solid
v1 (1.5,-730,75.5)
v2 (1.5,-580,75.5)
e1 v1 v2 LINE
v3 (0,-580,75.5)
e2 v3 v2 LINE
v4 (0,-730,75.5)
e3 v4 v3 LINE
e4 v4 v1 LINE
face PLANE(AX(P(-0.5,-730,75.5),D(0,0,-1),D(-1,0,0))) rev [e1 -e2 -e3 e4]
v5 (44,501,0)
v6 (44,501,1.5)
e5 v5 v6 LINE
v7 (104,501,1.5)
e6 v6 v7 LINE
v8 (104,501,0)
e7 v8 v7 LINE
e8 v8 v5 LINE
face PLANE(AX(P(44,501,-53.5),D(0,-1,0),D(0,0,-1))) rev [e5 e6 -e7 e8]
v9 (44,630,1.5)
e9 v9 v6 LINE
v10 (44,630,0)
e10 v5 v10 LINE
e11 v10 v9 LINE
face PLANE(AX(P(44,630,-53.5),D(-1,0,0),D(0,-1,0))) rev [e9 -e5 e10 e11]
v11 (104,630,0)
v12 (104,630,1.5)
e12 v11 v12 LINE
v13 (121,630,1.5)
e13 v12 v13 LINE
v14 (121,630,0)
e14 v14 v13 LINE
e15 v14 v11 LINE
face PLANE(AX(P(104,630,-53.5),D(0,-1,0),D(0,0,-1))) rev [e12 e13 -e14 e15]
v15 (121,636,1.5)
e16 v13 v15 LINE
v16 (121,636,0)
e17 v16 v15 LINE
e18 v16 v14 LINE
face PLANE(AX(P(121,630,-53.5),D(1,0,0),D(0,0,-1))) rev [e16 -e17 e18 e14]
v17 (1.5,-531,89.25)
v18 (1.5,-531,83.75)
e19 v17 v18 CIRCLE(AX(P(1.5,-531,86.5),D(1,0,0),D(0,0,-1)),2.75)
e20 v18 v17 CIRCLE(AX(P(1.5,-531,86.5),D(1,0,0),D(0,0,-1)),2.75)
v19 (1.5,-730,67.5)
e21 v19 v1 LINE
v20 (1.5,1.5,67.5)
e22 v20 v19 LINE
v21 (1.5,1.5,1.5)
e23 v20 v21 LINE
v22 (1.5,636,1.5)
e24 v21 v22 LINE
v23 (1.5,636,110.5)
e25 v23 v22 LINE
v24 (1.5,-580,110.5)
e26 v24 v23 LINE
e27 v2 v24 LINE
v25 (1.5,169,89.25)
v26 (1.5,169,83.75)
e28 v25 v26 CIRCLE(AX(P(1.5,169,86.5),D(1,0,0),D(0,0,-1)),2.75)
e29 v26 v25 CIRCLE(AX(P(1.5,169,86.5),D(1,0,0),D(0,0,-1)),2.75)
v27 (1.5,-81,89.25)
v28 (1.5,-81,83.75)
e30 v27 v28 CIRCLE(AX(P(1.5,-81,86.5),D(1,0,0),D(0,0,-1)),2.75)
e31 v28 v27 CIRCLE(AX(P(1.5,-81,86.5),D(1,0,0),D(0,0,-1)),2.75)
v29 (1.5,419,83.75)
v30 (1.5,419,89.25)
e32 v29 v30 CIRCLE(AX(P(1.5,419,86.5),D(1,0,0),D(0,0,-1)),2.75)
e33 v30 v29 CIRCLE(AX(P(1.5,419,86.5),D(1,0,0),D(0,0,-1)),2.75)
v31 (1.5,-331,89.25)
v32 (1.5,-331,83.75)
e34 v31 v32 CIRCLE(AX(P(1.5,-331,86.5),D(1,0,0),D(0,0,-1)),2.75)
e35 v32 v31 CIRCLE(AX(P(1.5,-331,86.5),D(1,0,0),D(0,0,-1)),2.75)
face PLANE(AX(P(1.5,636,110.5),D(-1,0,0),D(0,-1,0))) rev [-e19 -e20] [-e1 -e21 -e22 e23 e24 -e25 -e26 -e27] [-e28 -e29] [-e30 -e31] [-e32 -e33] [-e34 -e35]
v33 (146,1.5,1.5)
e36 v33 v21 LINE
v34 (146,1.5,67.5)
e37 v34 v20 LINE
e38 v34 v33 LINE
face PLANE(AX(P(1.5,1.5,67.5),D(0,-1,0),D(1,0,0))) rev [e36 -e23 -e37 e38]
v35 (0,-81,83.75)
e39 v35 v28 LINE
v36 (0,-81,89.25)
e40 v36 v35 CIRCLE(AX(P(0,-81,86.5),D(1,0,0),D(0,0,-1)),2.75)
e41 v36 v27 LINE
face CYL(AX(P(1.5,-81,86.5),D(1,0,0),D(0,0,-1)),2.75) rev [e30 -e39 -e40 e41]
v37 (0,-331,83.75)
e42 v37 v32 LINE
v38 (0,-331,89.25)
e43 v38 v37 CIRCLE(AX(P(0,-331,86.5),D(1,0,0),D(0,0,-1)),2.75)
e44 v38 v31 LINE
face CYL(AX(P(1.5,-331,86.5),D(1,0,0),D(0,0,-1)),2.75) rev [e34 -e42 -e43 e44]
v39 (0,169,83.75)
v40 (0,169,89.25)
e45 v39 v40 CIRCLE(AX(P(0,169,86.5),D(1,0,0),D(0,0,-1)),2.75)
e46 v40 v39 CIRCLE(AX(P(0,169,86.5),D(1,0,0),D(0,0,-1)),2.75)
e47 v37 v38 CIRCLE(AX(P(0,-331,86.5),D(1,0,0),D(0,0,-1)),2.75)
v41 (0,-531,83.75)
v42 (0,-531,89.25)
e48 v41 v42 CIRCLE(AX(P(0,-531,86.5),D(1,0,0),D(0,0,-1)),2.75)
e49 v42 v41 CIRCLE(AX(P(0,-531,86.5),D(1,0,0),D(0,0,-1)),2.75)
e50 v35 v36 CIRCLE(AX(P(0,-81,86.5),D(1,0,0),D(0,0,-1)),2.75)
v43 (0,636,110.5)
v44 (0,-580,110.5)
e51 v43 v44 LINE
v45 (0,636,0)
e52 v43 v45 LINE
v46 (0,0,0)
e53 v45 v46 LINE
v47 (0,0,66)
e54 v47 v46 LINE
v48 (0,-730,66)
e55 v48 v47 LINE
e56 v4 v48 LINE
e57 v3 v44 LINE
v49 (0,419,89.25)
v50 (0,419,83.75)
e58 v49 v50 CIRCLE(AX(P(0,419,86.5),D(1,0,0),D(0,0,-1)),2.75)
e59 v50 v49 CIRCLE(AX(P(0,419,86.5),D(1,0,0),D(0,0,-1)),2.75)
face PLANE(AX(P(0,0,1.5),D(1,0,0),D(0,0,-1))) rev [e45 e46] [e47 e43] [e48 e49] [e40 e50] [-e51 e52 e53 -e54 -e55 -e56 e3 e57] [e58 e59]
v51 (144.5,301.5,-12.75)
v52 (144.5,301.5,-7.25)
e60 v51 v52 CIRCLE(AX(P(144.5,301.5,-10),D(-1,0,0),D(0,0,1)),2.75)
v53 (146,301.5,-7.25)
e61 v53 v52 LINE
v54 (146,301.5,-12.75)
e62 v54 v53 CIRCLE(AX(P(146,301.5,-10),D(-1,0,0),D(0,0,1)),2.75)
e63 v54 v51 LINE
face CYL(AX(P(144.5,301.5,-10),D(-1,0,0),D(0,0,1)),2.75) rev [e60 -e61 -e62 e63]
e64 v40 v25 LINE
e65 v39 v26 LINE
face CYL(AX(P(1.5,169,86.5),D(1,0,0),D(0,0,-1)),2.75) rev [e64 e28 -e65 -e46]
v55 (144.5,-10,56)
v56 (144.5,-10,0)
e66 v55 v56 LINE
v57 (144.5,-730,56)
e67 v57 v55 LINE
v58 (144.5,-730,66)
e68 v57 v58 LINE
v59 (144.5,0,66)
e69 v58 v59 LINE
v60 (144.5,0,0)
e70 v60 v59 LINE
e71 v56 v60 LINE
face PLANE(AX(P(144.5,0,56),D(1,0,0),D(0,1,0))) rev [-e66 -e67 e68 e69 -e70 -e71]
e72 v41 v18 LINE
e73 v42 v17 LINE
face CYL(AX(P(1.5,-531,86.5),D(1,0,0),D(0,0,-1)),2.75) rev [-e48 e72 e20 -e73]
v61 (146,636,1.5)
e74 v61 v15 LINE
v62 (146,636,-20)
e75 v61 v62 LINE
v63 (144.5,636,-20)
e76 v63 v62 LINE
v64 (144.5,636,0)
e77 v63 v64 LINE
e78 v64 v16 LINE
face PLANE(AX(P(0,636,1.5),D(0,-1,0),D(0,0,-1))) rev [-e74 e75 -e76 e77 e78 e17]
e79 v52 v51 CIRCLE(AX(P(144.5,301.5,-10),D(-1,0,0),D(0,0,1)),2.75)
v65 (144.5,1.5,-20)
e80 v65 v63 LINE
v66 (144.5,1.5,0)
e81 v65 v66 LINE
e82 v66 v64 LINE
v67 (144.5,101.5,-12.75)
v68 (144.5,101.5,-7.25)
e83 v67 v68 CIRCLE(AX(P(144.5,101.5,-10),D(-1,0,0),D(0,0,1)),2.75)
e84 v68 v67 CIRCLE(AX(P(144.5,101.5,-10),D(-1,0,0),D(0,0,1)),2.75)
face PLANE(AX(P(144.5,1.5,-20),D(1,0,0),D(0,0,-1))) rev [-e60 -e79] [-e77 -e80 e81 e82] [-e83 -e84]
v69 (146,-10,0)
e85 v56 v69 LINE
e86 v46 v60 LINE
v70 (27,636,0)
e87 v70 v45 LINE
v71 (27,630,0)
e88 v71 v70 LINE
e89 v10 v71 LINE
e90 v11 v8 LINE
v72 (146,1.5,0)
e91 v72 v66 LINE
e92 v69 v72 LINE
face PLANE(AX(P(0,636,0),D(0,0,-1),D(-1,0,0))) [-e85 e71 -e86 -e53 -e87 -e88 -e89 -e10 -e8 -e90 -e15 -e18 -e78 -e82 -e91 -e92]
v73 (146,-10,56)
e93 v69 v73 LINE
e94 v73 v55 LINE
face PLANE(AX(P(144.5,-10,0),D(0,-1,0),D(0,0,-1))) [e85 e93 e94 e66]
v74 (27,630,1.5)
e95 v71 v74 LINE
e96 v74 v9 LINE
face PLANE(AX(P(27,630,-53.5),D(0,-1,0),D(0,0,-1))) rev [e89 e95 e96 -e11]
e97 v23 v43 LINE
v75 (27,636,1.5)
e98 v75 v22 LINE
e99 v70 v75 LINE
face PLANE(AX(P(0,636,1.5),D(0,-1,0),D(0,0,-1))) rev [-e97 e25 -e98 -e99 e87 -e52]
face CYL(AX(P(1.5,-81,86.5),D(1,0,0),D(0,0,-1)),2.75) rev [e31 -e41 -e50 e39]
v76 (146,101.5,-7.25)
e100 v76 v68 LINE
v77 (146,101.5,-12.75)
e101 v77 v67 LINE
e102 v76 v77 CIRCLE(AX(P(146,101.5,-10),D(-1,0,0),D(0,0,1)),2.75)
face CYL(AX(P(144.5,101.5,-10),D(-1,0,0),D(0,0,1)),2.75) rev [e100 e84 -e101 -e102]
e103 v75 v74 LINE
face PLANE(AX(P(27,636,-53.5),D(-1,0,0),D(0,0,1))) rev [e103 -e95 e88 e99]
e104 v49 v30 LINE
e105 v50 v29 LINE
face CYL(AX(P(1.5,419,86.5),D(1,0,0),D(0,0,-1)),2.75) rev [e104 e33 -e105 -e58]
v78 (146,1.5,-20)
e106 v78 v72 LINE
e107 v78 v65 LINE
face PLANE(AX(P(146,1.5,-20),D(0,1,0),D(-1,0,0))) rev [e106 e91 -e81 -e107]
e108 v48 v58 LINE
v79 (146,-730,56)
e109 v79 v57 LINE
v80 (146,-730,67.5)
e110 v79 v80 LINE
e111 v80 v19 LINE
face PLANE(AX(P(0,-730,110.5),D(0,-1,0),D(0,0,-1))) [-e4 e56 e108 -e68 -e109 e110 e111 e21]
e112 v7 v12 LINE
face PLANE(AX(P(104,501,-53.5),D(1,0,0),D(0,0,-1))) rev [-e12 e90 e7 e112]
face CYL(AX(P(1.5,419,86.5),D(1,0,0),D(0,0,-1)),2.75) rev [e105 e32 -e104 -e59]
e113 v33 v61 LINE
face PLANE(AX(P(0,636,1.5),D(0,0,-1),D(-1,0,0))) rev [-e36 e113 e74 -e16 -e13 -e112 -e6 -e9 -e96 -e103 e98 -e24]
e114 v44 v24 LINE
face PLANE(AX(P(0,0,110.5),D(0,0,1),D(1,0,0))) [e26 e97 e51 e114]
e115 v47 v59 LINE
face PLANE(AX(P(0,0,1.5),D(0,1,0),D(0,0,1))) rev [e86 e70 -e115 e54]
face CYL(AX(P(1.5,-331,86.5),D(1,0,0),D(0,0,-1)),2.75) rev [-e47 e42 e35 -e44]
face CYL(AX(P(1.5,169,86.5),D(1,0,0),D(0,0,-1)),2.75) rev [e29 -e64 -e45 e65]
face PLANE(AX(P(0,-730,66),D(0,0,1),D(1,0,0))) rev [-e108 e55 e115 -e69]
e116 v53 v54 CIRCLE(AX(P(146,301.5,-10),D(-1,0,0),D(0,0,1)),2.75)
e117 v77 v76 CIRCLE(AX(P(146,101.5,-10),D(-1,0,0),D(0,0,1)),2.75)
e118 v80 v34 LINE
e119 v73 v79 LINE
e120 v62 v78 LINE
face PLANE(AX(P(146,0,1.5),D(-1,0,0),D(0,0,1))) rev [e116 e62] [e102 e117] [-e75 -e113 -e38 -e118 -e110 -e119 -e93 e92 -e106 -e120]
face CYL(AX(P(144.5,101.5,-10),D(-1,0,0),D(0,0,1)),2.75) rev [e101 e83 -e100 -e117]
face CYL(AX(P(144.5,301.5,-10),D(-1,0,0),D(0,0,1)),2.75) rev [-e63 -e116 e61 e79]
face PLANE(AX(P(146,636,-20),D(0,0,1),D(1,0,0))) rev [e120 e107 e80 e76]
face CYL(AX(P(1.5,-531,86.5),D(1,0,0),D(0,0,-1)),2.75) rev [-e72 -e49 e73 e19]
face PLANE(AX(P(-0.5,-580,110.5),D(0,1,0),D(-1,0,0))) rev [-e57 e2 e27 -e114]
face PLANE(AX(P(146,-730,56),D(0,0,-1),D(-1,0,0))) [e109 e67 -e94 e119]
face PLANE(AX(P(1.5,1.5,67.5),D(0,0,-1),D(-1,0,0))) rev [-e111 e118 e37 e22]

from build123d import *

# Parameters (mm, degrees)
SKETCH_1_W                  = 146
SKETCH_1_H                  = 636
EXTRUDE_1_DEPTH             = 1.5
SKETCH_2_W                  = 1.5
SKETCH_2_H                  = 636
EXTRUDE_2_DEPTH             = 109
SKETCH_4_W                  = 144.5
SKETCH_4_H                  = 1.5
EXTRUDE_4_DEPTH             = 66
EXTRUDE_5_DEPTH             = 730
SKETCH_6_W                  = 1.5
SKETCH_6_H                  = 634.5
EXTRUDE_6_DEPTH             = 20
SKETCH_7_W                  = 1.5
SKETCH_7_H                  = 730
EXTRUDE_7_DEPTH             = 10
SKETCH_8_W                  = 1.5
SKETCH_8_H                  = 56
EXTRUDE_8_DEPTH             = 10
SKETCH_10_W                 = 35
SKETCH_10_H                 = 150
CUT_EXTRUDE_2_DEPTH         = 2
HOLE_WIZARD_5_5_5_5_1_D     = 5.5
HOLE_WIZARD_5_5_5_5_2_D     = 5.5
HOLE_WIZARD_5_5_5_5_2_DEPTH = 1.5
HOLE_WIZARD_5_5_5_5_2_TIP   = 1.652366702
CUT_EXTRUDE_3_DEPTH         = 55


with BuildPart() as part:
    # 草图1 → 凸台-拉伸1 (new body)
    with BuildSketch(Plane.XY):
        with Locations((73, 318)):
            Rectangle(SKETCH_1_W, SKETCH_1_H)
    extrude(amount=EXTRUDE_1_DEPTH)

    # 草图2 → 凸台-拉伸2 (add)
    with BuildSketch(Plane.XY.offset(1.5)):
        with Locations((0.75, 318)):
            Rectangle(SKETCH_2_W, SKETCH_2_H)
    extrude(amount=EXTRUDE_2_DEPTH)

    # 草图4 → 凸台-拉伸4 (add)
    with BuildSketch(Plane.XY.offset(1.5)):
        with Locations((73.75, 0.75)):
            Rectangle(SKETCH_4_W, SKETCH_4_H)
    extrude(amount=EXTRUDE_4_DEPTH)

    # 草图5 → 凸台-拉伸5 (add)
    with BuildSketch(Plane.XZ):
        Polygon((0, 110.5), (0, 66), (146, 66), (146, 67.5), (1.5, 67.5), (1.5, 110.5), align=None)
    extrude(amount=EXTRUDE_5_DEPTH)

    # 草图6 → 凸台-拉伸6 (add)
    with BuildSketch(Plane(origin=(0, 0, 0), x_dir=(-1, 0, 0), z_dir=(0, 0, -1))):
        with Locations((-145.25, 318.75)):
            Rectangle(SKETCH_6_W, SKETCH_6_H)
    extrude(amount=EXTRUDE_6_DEPTH)

    # 草图7 → 凸台-拉伸7 (add)
    with BuildSketch(Plane(origin=(0, 0, 66), x_dir=(-1, 0, 0), z_dir=(0, 0, -1))):
        with Locations((-145.25, -365)):
            Rectangle(SKETCH_7_W, SKETCH_7_H)
    extrude(amount=EXTRUDE_7_DEPTH)

    # 草图8 → 凸台-拉伸8 (add)
    with BuildSketch(Plane.XZ):
        with Locations((145.25, 28)):
            Rectangle(SKETCH_8_W, SKETCH_8_H)
    extrude(amount=EXTRUDE_8_DEPTH)

    # 草图10 → 切除-拉伸2 (cut)
    with BuildSketch(Plane(origin=(1.5, 0, 0), x_dir=(0, 0, -1), z_dir=(1, 0, 0))):
        with Locations((-93, -655)):
            Rectangle(SKETCH_10_W, SKETCH_10_H)
    extrude(amount=-CUT_EXTRUDE_2_DEPTH, mode=Mode.SUBTRACT)

    # Ø5.5 (5.5) 直径孔1 (through all)
    with Locations(Plane(origin=(1.5, 0, 0), x_dir=(0, 0, -1), z_dir=(1, 0, 0))):
        with Locations((-86.5, 419), (-86.5, 169), (-86.5, -81), (-86.5, -331), (-86.5, -531)):
            Hole(HOLE_WIZARD_5_5_5_5_1_D / 2)

    # Ø5.5 (5.5) 直径孔2
    with Locations(Plane.ZY.offset(-144.5)):
        with Locations((-10, 301.5), (-10, 101.5)):
            Hole(HOLE_WIZARD_5_5_5_5_2_D / 2, depth=HOLE_WIZARD_5_5_5_5_2_DEPTH)
            with Locations((0, 0, -(HOLE_WIZARD_5_5_5_5_2_DEPTH + HOLE_WIZARD_5_5_5_5_2_TIP / 2))):  # 118° drill point
                Cone(0, HOLE_WIZARD_5_5_5_5_2_D / 2, HOLE_WIZARD_5_5_5_5_2_TIP, mode=Mode.SUBTRACT)

    # 草图15 → 切除-拉伸3 (cut)
    with BuildSketch(Plane.XY.offset(1.5)):
        Polygon((27, 636), (27, 630), (44, 630), (44, 501), (104, 501), (104, 630), (121, 630), (121, 636), align=None)
    extrude(amount=-CUT_EXTRUDE_3_DEPTH, mode=Mode.SUBTRACT)


solid = part.part
